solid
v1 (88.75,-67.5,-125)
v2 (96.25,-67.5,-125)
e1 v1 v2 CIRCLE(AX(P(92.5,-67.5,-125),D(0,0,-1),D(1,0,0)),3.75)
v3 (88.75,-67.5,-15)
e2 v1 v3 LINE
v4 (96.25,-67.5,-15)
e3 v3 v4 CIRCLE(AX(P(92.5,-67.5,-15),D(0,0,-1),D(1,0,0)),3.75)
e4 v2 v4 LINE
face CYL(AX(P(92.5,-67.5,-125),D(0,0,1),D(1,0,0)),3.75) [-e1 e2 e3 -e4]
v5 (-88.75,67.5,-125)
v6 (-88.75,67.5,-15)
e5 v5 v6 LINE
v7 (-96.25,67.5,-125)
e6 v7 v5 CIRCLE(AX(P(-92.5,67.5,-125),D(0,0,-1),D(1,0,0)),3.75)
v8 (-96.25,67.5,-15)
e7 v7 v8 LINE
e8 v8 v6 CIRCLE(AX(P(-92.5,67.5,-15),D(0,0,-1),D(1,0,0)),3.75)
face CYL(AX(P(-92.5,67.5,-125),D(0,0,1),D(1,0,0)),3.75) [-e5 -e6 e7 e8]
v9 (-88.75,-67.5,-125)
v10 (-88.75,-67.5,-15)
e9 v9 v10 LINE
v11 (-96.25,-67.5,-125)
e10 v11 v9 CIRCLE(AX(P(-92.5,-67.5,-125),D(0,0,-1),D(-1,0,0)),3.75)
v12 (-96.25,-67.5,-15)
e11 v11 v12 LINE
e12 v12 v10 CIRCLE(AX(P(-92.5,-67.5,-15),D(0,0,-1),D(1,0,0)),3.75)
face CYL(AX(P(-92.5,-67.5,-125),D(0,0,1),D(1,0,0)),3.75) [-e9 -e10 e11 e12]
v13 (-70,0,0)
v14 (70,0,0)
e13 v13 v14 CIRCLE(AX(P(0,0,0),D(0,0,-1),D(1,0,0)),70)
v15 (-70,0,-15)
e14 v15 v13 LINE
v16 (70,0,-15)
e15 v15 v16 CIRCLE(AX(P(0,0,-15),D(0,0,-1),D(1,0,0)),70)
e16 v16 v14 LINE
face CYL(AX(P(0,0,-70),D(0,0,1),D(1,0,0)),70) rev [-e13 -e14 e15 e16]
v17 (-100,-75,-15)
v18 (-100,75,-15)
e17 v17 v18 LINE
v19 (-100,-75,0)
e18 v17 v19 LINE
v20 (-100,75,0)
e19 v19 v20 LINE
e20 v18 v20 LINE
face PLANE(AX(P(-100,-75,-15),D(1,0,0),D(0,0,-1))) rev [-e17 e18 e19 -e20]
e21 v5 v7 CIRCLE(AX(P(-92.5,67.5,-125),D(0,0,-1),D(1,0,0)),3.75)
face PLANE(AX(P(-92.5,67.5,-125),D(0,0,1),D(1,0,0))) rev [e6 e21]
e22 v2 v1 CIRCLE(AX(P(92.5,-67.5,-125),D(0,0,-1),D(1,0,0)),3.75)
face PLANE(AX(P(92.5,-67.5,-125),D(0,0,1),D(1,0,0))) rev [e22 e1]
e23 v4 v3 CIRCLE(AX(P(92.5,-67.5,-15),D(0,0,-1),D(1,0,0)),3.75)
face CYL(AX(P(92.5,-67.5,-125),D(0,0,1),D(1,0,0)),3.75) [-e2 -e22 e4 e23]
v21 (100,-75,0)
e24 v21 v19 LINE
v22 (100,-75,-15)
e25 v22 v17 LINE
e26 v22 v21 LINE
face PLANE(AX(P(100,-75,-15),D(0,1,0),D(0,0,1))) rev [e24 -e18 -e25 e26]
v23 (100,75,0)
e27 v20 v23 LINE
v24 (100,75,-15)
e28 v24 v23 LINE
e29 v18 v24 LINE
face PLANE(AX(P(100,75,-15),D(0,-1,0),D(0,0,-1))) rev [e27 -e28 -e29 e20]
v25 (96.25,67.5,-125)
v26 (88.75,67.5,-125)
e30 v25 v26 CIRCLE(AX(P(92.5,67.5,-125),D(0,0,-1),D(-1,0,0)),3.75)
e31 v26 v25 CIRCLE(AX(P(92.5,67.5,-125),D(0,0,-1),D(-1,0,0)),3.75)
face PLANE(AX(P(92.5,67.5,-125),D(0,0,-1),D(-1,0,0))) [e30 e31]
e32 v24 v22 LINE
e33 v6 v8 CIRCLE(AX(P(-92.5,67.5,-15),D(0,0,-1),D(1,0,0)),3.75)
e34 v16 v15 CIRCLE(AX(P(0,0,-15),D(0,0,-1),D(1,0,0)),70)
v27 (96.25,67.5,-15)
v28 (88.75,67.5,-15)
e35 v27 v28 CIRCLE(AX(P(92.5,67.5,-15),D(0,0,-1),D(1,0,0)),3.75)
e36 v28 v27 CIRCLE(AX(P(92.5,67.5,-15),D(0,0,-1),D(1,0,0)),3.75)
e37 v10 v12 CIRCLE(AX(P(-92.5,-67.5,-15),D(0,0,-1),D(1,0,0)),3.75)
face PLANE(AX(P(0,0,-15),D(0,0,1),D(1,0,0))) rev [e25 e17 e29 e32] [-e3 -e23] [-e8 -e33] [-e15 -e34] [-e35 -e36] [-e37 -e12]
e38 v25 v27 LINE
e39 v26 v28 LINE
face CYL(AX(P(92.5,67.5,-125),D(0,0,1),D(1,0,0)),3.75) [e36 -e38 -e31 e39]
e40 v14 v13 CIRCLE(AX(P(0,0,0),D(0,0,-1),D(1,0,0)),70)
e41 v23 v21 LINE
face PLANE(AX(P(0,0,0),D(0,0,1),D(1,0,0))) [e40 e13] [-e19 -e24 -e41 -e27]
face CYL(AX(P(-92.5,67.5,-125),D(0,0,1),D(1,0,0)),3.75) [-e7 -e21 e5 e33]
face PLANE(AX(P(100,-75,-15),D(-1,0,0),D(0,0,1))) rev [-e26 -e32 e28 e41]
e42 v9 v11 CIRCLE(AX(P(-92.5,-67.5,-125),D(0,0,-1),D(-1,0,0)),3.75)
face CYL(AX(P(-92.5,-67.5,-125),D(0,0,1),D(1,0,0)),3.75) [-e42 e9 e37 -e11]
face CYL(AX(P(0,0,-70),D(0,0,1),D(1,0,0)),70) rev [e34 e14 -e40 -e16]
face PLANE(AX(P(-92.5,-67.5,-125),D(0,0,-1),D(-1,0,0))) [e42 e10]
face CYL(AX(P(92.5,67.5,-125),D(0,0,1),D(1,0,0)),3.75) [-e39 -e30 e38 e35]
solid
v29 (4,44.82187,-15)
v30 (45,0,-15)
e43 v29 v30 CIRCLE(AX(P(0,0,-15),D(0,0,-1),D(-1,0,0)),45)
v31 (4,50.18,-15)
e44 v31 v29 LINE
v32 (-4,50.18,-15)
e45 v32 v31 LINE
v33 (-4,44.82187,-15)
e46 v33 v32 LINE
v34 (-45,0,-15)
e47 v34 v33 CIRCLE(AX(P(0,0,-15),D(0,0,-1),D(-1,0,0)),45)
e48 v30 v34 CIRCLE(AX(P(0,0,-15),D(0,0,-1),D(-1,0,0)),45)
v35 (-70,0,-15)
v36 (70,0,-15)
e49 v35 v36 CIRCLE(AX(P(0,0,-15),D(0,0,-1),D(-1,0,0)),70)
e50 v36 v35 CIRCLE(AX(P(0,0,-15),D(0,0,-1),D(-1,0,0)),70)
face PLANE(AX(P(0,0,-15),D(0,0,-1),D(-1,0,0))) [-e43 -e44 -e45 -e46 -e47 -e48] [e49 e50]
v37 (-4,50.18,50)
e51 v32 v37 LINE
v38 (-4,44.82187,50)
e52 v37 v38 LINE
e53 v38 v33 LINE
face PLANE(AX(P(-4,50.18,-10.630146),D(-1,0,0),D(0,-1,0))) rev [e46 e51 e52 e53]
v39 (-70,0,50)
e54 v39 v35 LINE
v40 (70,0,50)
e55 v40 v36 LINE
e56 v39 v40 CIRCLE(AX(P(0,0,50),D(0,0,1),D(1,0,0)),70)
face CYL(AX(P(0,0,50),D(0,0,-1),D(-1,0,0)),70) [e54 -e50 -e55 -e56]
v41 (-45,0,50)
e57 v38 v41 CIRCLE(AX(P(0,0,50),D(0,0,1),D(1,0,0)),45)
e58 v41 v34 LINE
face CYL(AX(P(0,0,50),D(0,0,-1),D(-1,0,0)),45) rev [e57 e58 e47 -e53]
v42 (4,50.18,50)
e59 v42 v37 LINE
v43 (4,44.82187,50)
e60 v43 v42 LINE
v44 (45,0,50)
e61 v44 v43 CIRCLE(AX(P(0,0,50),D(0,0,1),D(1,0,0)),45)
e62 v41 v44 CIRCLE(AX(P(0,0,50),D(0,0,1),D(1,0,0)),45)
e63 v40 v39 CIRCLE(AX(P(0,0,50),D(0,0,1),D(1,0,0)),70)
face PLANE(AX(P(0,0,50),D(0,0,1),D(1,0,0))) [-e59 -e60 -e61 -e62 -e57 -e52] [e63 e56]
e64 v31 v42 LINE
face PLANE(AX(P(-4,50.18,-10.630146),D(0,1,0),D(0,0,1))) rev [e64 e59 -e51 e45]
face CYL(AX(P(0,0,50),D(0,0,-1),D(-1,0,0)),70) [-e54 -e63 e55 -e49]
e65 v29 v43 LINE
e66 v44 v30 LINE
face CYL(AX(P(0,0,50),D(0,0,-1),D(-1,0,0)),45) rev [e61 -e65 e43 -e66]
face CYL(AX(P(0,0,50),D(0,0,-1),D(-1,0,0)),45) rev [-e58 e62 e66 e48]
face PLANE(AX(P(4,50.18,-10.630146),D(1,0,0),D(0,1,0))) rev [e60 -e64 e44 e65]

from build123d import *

# Parameters (mm, degrees)
SKETCH2_R           = 70
SKETCH2_R_2         = 45
BOSS_EXTRUDE1_DEPTH = 50
SKETCH3_W           = 200
SKETCH3_H           = 150
BOSS_EXTRUDE2_DEPTH = 15
SKETCH4_R           = 3.75
BOSS_EXTRUDE3_DEPTH = 110
SKETCH5_W           = 8
SKETCH5_H           = 7
CUT_EXTRUDE1_DEPTH  = 50
CUT_EXTRUDE3_START  = -70
SKETCH6_R           = 70
CUT_EXTRUDE3_DEPTH  = 70
SKETCH9_R           = 70
BOSS_EXTRUDE4_DEPTH = 15


with BuildPart() as part:
    # Sketch2 → Boss-Extrude1 (new body)
    with BuildSketch(Plane.XY):
        Circle(SKETCH2_R)
        Circle(SKETCH2_R_2, mode=Mode.SUBTRACT)
    extrude(amount=BOSS_EXTRUDE1_DEPTH)

    # Sketch3 → Boss-Extrude2 (add)
    with BuildSketch(Plane(origin=(0, 0, 0), x_dir=(-1, 0, 0), z_dir=(0, 0, -1))):
        Rectangle(SKETCH3_W, SKETCH3_H)
    extrude(amount=BOSS_EXTRUDE2_DEPTH)

    # Sketch4 → Boss-Extrude3 (add)
    with BuildSketch(Plane(origin=(0, 0, -15), x_dir=(-1, 0, 0), z_dir=(0, 0, -1))):
        with Locations(Location((-92.5, 67.5, 0), (0, 0, 180))):
            Circle(SKETCH4_R)
        with Locations(Location((92.5, 67.5, 0), (0, 0, 180))):
            Circle(SKETCH4_R)
        with Locations(Location((92.5, -67.5, 0), (0, 0, 180))):
            Circle(SKETCH4_R)
        with Locations(Location((-92.5, -67.5, 0), (0, 0, 180))):
            Circle(SKETCH4_R)
    extrude(amount=BOSS_EXTRUDE3_DEPTH)

    # Sketch5 → Cut-Extrude1 (cut)
    with BuildSketch(Plane.XY.offset(50)):
        with Locations((0, 46.68)):
            Rectangle(SKETCH5_W, SKETCH5_H)
    extrude(amount=-CUT_EXTRUDE1_DEPTH, mode=Mode.SUBTRACT)

    # Sketch6 → Cut-Extrude3 (cut)
    with BuildSketch(Plane.XY.offset(CUT_EXTRUDE3_START)):
        Circle(SKETCH6_R)
    extrude(amount=CUT_EXTRUDE3_DEPTH, mode=Mode.SUBTRACT)


with BuildPart() as cut_extrude3_piece_1:
    # of the separate pieces the step leaves, piece 1, a body of its own (cut_extrude3_pieces)
    add(part.part.solids().sort_by_distance((70, 0, 50))[0])

    # Sketch9 → Boss-Extrude4 (add)
    with BuildSketch(Plane(origin=(0, 0, 0), x_dir=(-1, 0, 0), z_dir=(0, 0, -1))):
        with Locations(Location((0, 0, 0), (0, 0, 180))):
            Circle(SKETCH9_R)
        with BuildLine():
            Line((4, 44.821869662), (4, 50.18))
            Line((4, 50.18), (-4, 50.18))
            Line((-4, 50.18), (-4, 44.821869662))
            ThreePointArc((-4, 44.821869662), (0, -45), (4, 44.821869662))
        make_face(mode=Mode.SUBTRACT)
    extrude(amount=BOSS_EXTRUDE4_DEPTH)


with BuildPart() as cut_extrude3_piece_2:
    # of the separate pieces the step leaves, piece 2, a body of its own (cut_extrude3_pieces)
    add(part.part.solids().sort_by_distance((100, -75, 0))[0])


solid = Compound([cut_extrude3_piece_1.part, cut_extrude3_piece_2.part])
